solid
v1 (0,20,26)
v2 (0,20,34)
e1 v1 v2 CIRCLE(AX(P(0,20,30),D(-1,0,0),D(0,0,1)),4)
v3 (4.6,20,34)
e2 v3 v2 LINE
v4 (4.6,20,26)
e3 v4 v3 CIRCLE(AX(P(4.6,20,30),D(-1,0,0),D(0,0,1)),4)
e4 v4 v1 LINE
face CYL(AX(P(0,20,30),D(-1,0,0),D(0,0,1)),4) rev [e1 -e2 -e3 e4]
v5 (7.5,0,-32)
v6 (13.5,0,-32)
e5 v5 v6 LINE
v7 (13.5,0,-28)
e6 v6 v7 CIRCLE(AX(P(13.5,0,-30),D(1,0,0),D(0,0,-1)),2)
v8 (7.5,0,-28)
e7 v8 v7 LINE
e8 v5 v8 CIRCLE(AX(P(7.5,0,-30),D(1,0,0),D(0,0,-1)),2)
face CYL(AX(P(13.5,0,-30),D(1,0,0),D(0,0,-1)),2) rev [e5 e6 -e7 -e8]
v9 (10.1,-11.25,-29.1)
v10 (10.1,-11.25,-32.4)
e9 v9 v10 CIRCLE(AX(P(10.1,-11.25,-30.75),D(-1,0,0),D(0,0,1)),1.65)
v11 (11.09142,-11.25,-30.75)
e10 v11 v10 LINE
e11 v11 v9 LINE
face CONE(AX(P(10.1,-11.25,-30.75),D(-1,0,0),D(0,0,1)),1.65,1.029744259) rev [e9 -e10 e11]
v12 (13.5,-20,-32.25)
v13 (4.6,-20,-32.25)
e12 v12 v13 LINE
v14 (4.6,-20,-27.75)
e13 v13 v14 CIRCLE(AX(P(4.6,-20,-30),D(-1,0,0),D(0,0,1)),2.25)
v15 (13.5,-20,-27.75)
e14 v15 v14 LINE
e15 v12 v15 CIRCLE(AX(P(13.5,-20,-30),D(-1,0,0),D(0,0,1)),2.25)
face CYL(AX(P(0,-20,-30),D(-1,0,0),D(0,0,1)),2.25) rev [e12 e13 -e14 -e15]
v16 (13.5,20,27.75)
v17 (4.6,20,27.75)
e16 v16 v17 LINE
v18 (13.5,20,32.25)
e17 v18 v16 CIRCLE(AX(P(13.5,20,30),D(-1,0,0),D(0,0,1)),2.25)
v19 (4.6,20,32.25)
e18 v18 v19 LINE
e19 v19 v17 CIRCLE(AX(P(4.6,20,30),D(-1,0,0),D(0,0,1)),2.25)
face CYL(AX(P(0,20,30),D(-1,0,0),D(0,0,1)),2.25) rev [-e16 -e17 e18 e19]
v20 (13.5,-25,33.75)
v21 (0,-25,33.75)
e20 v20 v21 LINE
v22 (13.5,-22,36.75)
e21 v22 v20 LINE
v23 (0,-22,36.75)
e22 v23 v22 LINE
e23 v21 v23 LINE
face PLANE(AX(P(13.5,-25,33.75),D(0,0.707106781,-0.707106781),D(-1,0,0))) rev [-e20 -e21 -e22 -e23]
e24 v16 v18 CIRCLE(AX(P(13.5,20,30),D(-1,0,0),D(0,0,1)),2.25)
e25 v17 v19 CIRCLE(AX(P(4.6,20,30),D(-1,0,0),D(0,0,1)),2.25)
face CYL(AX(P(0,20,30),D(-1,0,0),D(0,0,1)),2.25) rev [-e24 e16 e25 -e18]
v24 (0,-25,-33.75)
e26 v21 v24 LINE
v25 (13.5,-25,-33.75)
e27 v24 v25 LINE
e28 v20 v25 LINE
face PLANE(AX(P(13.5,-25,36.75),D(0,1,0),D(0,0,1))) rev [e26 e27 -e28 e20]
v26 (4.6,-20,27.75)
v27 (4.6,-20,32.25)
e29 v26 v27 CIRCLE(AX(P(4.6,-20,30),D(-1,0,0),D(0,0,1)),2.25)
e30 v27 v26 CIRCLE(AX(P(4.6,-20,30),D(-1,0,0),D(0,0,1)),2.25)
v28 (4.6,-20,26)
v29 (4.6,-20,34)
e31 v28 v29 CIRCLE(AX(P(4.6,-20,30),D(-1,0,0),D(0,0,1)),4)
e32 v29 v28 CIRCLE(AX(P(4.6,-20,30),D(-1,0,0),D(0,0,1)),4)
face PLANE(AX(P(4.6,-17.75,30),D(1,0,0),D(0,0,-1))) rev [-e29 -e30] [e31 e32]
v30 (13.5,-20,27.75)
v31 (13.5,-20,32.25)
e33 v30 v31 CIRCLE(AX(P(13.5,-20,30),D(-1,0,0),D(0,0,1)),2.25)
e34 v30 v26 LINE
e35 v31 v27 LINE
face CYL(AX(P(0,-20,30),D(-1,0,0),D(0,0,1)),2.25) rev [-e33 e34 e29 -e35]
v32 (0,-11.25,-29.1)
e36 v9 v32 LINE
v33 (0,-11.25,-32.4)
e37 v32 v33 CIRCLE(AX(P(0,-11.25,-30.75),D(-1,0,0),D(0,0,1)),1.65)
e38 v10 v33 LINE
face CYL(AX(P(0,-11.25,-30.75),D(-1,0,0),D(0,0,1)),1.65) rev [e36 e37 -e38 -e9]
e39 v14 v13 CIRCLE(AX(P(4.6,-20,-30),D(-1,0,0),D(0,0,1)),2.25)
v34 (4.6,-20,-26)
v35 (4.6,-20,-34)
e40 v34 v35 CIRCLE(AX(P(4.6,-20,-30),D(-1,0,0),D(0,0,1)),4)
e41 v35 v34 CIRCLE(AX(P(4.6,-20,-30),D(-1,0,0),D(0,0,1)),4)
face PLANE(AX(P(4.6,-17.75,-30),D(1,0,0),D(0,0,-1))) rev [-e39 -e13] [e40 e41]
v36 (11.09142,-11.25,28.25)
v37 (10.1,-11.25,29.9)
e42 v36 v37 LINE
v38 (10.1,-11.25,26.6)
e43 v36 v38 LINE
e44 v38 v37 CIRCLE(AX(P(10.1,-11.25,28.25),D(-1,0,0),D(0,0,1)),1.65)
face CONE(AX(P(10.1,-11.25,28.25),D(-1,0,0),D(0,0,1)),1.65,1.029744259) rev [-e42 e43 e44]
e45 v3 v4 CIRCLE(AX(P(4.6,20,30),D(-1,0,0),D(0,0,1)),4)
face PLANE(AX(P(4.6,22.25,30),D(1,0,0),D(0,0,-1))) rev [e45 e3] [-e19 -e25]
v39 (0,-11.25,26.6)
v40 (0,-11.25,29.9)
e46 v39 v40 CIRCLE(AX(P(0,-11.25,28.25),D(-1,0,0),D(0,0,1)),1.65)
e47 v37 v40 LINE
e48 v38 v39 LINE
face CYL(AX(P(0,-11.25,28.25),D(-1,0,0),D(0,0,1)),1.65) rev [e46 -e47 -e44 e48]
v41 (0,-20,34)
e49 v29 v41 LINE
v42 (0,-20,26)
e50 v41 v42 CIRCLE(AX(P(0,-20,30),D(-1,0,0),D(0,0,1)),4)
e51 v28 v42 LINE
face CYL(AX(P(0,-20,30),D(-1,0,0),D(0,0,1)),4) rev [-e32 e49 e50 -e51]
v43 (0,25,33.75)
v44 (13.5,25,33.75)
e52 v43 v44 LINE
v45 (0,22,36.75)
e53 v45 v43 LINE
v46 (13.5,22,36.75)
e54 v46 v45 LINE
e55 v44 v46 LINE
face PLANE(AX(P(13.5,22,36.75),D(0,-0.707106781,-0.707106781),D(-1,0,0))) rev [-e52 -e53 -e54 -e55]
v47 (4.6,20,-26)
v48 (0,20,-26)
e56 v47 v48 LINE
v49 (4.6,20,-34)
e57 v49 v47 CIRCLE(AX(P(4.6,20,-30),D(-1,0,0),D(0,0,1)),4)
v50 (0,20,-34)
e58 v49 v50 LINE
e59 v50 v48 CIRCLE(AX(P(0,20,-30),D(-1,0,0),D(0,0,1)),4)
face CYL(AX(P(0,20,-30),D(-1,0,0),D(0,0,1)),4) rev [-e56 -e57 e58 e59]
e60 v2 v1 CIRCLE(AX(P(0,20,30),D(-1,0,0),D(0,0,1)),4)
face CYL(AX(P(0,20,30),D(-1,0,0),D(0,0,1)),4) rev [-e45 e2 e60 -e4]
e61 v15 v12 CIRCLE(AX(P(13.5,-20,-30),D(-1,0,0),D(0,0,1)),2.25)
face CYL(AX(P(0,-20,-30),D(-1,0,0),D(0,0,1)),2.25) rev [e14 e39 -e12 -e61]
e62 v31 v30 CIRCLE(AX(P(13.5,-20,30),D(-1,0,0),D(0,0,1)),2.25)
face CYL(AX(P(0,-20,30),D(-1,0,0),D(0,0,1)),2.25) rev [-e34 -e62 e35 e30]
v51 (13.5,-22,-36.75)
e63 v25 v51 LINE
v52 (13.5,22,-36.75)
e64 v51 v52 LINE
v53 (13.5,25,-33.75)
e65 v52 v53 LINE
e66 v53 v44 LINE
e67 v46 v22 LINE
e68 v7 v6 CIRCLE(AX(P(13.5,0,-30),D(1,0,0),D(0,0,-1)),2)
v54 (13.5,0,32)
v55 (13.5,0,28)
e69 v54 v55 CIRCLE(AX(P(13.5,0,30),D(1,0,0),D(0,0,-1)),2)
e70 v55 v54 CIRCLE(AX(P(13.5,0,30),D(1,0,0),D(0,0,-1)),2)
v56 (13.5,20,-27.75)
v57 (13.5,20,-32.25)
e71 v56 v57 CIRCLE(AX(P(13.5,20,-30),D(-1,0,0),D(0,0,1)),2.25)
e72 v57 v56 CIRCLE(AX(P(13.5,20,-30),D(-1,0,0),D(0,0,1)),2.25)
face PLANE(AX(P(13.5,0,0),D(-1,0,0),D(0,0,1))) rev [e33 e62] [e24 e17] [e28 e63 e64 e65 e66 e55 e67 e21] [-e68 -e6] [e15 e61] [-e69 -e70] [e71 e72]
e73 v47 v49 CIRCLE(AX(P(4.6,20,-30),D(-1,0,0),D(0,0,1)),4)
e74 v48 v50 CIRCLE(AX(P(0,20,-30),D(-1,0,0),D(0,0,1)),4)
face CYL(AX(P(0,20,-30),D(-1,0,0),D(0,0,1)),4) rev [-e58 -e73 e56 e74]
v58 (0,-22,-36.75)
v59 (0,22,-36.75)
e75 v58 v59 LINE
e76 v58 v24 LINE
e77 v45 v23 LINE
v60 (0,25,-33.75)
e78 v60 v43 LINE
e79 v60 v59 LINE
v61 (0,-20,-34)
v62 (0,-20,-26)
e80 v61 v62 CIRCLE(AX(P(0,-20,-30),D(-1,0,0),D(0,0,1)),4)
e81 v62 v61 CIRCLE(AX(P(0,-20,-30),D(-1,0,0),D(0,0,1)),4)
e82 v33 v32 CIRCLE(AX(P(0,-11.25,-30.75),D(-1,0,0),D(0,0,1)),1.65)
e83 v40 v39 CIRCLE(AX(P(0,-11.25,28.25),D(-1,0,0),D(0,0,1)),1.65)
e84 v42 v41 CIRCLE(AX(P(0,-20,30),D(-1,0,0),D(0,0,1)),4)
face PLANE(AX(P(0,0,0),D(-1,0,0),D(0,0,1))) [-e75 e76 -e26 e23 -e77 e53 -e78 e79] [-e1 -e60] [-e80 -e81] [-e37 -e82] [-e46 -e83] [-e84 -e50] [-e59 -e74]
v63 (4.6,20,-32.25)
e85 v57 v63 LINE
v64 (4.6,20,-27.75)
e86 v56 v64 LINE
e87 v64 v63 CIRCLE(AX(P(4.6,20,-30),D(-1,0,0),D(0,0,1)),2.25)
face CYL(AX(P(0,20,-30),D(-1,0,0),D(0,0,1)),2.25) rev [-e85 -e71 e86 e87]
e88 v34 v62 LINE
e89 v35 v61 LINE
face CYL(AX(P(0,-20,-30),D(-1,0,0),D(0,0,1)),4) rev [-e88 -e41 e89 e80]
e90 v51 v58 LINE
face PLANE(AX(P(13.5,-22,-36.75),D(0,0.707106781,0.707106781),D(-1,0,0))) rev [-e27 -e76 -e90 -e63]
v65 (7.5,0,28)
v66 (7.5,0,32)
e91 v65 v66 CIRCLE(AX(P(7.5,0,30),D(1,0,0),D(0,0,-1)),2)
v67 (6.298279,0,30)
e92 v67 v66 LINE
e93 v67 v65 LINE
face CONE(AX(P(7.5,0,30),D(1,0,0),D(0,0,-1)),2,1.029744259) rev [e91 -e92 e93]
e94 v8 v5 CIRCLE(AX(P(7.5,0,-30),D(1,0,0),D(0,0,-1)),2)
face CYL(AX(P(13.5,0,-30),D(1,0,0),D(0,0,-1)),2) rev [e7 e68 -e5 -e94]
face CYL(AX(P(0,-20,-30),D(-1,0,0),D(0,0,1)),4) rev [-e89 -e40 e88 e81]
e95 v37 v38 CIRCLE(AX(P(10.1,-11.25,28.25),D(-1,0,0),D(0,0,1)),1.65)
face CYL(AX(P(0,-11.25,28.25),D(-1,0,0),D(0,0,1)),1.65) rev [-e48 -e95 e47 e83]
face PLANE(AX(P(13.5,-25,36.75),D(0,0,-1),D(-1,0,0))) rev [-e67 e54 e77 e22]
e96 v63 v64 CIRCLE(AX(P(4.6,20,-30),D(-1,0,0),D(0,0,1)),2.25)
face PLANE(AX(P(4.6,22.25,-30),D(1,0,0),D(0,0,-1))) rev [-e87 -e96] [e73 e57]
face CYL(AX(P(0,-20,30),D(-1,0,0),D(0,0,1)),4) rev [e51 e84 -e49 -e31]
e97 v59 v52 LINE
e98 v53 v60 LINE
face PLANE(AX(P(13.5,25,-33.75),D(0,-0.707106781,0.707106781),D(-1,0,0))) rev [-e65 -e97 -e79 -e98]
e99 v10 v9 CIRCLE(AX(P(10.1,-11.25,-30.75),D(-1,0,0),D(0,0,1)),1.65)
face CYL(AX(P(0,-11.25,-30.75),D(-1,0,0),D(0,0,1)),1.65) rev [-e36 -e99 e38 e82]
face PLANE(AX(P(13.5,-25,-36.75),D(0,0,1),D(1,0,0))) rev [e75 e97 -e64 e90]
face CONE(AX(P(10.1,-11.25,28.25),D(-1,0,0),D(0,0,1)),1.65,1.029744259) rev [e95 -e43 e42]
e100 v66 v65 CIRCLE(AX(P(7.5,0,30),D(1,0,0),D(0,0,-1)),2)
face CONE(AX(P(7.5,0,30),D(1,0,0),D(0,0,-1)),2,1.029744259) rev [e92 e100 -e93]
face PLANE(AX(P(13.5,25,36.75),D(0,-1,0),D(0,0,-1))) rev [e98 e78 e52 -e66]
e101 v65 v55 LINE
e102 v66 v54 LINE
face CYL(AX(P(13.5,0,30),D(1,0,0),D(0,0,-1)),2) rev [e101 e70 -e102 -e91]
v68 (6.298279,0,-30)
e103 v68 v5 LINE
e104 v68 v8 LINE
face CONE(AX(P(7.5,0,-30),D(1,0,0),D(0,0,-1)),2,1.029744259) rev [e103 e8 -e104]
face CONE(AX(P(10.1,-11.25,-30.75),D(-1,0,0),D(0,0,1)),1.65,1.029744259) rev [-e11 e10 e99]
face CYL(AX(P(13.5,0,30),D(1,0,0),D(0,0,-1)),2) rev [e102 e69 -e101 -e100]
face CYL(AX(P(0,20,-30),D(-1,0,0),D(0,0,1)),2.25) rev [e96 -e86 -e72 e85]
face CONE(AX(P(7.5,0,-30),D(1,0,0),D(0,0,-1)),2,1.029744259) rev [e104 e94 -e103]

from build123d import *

# Parameters (mm, degrees)
SKETCH1_W                                            = 73.5
SKETCH1_H                                            = 50
BOSS_EXTRUDE1_DEPTH                                  = 13.5
CBORE_FOR_M4_HEXAGON_SOCKET_HEAD_CAP_SCR_D           = 4.5
CBORE_FOR_M4_HEXAGON_SOCKET_HEAD_CAP_SCR_CBORE_D     = 8
CBORE_FOR_M4_HEXAGON_SOCKET_HEAD_CAP_SCR_CBORE_DEPTH = 4.6
F_4_0MM_DOWEL_HOLE1_D                                = 4
F_4_0MM_DOWEL_HOLE1_DEPTH                            = 6
F_4_0MM_DOWEL_HOLE1_TIP                              = 1.201721238
M4_TAPPED_HOLE1_D                                    = 3.3
M4_TAPPED_HOLE1_DEPTH                                = 10.1
M4_TAPPED_HOLE1_TIP                                  = 0.991420021
CHAMFER1_SIZE                                        = 3


with BuildPart() as part:
    # Sketch1 → Boss-Extrude1 (new body)
    with BuildSketch(Plane(origin=(0, 0, 0), x_dir=(0, 0, -1), z_dir=(1, 0, 0))):
        Rectangle(SKETCH1_W, SKETCH1_H)
    extrude(amount=BOSS_EXTRUDE1_DEPTH)

    # CBORE for M4 Hexagon socket head cap screws1 (through all)
    with Locations(Plane.ZY):
        with Locations((30, -20), (30, 20), (-30, 20), (-30, -20)):
            CounterBoreHole(CBORE_FOR_M4_HEXAGON_SOCKET_HEAD_CAP_SCR_D / 2, CBORE_FOR_M4_HEXAGON_SOCKET_HEAD_CAP_SCR_CBORE_D / 2, CBORE_FOR_M4_HEXAGON_SOCKET_HEAD_CAP_SCR_CBORE_DEPTH)

    # Ø4.0mm Dowel Hole1
    with Locations(Plane(origin=(13.5, 0, 0), x_dir=(0, 0, -1), z_dir=(1, 0, 0))):
        with Locations((30, 0), (-30, 0)):
            Hole(F_4_0MM_DOWEL_HOLE1_D / 2, depth=F_4_0MM_DOWEL_HOLE1_DEPTH)
            with Locations((0, 0, -(F_4_0MM_DOWEL_HOLE1_DEPTH + F_4_0MM_DOWEL_HOLE1_TIP / 2))):  # 118° drill point
                Cone(0, F_4_0MM_DOWEL_HOLE1_D / 2, F_4_0MM_DOWEL_HOLE1_TIP, mode=Mode.SUBTRACT)

    # M4 Tapped Hole1
    with Locations(Plane.ZY):
        with Locations((28.25, -11.25), (-30.75, -11.25)):
            Hole(M4_TAPPED_HOLE1_D / 2, depth=M4_TAPPED_HOLE1_DEPTH)
            with Locations((0, 0, -(M4_TAPPED_HOLE1_DEPTH + M4_TAPPED_HOLE1_TIP / 2))):  # 118° drill point
                Cone(0, M4_TAPPED_HOLE1_D / 2, M4_TAPPED_HOLE1_TIP, mode=Mode.SUBTRACT)

    # Chamfer1
    chamfer1_edges = [part.edges().sort_by_distance(p)[0] for p in [
        (6.75, -25, -36.75),
        (6.75, -25, 36.75),
        (6.75, 25, 36.75),
        (6.75, 25, -36.75),
    ]]
    chamfer(chamfer1_edges, length=CHAMFER1_SIZE)


solid = part.part
